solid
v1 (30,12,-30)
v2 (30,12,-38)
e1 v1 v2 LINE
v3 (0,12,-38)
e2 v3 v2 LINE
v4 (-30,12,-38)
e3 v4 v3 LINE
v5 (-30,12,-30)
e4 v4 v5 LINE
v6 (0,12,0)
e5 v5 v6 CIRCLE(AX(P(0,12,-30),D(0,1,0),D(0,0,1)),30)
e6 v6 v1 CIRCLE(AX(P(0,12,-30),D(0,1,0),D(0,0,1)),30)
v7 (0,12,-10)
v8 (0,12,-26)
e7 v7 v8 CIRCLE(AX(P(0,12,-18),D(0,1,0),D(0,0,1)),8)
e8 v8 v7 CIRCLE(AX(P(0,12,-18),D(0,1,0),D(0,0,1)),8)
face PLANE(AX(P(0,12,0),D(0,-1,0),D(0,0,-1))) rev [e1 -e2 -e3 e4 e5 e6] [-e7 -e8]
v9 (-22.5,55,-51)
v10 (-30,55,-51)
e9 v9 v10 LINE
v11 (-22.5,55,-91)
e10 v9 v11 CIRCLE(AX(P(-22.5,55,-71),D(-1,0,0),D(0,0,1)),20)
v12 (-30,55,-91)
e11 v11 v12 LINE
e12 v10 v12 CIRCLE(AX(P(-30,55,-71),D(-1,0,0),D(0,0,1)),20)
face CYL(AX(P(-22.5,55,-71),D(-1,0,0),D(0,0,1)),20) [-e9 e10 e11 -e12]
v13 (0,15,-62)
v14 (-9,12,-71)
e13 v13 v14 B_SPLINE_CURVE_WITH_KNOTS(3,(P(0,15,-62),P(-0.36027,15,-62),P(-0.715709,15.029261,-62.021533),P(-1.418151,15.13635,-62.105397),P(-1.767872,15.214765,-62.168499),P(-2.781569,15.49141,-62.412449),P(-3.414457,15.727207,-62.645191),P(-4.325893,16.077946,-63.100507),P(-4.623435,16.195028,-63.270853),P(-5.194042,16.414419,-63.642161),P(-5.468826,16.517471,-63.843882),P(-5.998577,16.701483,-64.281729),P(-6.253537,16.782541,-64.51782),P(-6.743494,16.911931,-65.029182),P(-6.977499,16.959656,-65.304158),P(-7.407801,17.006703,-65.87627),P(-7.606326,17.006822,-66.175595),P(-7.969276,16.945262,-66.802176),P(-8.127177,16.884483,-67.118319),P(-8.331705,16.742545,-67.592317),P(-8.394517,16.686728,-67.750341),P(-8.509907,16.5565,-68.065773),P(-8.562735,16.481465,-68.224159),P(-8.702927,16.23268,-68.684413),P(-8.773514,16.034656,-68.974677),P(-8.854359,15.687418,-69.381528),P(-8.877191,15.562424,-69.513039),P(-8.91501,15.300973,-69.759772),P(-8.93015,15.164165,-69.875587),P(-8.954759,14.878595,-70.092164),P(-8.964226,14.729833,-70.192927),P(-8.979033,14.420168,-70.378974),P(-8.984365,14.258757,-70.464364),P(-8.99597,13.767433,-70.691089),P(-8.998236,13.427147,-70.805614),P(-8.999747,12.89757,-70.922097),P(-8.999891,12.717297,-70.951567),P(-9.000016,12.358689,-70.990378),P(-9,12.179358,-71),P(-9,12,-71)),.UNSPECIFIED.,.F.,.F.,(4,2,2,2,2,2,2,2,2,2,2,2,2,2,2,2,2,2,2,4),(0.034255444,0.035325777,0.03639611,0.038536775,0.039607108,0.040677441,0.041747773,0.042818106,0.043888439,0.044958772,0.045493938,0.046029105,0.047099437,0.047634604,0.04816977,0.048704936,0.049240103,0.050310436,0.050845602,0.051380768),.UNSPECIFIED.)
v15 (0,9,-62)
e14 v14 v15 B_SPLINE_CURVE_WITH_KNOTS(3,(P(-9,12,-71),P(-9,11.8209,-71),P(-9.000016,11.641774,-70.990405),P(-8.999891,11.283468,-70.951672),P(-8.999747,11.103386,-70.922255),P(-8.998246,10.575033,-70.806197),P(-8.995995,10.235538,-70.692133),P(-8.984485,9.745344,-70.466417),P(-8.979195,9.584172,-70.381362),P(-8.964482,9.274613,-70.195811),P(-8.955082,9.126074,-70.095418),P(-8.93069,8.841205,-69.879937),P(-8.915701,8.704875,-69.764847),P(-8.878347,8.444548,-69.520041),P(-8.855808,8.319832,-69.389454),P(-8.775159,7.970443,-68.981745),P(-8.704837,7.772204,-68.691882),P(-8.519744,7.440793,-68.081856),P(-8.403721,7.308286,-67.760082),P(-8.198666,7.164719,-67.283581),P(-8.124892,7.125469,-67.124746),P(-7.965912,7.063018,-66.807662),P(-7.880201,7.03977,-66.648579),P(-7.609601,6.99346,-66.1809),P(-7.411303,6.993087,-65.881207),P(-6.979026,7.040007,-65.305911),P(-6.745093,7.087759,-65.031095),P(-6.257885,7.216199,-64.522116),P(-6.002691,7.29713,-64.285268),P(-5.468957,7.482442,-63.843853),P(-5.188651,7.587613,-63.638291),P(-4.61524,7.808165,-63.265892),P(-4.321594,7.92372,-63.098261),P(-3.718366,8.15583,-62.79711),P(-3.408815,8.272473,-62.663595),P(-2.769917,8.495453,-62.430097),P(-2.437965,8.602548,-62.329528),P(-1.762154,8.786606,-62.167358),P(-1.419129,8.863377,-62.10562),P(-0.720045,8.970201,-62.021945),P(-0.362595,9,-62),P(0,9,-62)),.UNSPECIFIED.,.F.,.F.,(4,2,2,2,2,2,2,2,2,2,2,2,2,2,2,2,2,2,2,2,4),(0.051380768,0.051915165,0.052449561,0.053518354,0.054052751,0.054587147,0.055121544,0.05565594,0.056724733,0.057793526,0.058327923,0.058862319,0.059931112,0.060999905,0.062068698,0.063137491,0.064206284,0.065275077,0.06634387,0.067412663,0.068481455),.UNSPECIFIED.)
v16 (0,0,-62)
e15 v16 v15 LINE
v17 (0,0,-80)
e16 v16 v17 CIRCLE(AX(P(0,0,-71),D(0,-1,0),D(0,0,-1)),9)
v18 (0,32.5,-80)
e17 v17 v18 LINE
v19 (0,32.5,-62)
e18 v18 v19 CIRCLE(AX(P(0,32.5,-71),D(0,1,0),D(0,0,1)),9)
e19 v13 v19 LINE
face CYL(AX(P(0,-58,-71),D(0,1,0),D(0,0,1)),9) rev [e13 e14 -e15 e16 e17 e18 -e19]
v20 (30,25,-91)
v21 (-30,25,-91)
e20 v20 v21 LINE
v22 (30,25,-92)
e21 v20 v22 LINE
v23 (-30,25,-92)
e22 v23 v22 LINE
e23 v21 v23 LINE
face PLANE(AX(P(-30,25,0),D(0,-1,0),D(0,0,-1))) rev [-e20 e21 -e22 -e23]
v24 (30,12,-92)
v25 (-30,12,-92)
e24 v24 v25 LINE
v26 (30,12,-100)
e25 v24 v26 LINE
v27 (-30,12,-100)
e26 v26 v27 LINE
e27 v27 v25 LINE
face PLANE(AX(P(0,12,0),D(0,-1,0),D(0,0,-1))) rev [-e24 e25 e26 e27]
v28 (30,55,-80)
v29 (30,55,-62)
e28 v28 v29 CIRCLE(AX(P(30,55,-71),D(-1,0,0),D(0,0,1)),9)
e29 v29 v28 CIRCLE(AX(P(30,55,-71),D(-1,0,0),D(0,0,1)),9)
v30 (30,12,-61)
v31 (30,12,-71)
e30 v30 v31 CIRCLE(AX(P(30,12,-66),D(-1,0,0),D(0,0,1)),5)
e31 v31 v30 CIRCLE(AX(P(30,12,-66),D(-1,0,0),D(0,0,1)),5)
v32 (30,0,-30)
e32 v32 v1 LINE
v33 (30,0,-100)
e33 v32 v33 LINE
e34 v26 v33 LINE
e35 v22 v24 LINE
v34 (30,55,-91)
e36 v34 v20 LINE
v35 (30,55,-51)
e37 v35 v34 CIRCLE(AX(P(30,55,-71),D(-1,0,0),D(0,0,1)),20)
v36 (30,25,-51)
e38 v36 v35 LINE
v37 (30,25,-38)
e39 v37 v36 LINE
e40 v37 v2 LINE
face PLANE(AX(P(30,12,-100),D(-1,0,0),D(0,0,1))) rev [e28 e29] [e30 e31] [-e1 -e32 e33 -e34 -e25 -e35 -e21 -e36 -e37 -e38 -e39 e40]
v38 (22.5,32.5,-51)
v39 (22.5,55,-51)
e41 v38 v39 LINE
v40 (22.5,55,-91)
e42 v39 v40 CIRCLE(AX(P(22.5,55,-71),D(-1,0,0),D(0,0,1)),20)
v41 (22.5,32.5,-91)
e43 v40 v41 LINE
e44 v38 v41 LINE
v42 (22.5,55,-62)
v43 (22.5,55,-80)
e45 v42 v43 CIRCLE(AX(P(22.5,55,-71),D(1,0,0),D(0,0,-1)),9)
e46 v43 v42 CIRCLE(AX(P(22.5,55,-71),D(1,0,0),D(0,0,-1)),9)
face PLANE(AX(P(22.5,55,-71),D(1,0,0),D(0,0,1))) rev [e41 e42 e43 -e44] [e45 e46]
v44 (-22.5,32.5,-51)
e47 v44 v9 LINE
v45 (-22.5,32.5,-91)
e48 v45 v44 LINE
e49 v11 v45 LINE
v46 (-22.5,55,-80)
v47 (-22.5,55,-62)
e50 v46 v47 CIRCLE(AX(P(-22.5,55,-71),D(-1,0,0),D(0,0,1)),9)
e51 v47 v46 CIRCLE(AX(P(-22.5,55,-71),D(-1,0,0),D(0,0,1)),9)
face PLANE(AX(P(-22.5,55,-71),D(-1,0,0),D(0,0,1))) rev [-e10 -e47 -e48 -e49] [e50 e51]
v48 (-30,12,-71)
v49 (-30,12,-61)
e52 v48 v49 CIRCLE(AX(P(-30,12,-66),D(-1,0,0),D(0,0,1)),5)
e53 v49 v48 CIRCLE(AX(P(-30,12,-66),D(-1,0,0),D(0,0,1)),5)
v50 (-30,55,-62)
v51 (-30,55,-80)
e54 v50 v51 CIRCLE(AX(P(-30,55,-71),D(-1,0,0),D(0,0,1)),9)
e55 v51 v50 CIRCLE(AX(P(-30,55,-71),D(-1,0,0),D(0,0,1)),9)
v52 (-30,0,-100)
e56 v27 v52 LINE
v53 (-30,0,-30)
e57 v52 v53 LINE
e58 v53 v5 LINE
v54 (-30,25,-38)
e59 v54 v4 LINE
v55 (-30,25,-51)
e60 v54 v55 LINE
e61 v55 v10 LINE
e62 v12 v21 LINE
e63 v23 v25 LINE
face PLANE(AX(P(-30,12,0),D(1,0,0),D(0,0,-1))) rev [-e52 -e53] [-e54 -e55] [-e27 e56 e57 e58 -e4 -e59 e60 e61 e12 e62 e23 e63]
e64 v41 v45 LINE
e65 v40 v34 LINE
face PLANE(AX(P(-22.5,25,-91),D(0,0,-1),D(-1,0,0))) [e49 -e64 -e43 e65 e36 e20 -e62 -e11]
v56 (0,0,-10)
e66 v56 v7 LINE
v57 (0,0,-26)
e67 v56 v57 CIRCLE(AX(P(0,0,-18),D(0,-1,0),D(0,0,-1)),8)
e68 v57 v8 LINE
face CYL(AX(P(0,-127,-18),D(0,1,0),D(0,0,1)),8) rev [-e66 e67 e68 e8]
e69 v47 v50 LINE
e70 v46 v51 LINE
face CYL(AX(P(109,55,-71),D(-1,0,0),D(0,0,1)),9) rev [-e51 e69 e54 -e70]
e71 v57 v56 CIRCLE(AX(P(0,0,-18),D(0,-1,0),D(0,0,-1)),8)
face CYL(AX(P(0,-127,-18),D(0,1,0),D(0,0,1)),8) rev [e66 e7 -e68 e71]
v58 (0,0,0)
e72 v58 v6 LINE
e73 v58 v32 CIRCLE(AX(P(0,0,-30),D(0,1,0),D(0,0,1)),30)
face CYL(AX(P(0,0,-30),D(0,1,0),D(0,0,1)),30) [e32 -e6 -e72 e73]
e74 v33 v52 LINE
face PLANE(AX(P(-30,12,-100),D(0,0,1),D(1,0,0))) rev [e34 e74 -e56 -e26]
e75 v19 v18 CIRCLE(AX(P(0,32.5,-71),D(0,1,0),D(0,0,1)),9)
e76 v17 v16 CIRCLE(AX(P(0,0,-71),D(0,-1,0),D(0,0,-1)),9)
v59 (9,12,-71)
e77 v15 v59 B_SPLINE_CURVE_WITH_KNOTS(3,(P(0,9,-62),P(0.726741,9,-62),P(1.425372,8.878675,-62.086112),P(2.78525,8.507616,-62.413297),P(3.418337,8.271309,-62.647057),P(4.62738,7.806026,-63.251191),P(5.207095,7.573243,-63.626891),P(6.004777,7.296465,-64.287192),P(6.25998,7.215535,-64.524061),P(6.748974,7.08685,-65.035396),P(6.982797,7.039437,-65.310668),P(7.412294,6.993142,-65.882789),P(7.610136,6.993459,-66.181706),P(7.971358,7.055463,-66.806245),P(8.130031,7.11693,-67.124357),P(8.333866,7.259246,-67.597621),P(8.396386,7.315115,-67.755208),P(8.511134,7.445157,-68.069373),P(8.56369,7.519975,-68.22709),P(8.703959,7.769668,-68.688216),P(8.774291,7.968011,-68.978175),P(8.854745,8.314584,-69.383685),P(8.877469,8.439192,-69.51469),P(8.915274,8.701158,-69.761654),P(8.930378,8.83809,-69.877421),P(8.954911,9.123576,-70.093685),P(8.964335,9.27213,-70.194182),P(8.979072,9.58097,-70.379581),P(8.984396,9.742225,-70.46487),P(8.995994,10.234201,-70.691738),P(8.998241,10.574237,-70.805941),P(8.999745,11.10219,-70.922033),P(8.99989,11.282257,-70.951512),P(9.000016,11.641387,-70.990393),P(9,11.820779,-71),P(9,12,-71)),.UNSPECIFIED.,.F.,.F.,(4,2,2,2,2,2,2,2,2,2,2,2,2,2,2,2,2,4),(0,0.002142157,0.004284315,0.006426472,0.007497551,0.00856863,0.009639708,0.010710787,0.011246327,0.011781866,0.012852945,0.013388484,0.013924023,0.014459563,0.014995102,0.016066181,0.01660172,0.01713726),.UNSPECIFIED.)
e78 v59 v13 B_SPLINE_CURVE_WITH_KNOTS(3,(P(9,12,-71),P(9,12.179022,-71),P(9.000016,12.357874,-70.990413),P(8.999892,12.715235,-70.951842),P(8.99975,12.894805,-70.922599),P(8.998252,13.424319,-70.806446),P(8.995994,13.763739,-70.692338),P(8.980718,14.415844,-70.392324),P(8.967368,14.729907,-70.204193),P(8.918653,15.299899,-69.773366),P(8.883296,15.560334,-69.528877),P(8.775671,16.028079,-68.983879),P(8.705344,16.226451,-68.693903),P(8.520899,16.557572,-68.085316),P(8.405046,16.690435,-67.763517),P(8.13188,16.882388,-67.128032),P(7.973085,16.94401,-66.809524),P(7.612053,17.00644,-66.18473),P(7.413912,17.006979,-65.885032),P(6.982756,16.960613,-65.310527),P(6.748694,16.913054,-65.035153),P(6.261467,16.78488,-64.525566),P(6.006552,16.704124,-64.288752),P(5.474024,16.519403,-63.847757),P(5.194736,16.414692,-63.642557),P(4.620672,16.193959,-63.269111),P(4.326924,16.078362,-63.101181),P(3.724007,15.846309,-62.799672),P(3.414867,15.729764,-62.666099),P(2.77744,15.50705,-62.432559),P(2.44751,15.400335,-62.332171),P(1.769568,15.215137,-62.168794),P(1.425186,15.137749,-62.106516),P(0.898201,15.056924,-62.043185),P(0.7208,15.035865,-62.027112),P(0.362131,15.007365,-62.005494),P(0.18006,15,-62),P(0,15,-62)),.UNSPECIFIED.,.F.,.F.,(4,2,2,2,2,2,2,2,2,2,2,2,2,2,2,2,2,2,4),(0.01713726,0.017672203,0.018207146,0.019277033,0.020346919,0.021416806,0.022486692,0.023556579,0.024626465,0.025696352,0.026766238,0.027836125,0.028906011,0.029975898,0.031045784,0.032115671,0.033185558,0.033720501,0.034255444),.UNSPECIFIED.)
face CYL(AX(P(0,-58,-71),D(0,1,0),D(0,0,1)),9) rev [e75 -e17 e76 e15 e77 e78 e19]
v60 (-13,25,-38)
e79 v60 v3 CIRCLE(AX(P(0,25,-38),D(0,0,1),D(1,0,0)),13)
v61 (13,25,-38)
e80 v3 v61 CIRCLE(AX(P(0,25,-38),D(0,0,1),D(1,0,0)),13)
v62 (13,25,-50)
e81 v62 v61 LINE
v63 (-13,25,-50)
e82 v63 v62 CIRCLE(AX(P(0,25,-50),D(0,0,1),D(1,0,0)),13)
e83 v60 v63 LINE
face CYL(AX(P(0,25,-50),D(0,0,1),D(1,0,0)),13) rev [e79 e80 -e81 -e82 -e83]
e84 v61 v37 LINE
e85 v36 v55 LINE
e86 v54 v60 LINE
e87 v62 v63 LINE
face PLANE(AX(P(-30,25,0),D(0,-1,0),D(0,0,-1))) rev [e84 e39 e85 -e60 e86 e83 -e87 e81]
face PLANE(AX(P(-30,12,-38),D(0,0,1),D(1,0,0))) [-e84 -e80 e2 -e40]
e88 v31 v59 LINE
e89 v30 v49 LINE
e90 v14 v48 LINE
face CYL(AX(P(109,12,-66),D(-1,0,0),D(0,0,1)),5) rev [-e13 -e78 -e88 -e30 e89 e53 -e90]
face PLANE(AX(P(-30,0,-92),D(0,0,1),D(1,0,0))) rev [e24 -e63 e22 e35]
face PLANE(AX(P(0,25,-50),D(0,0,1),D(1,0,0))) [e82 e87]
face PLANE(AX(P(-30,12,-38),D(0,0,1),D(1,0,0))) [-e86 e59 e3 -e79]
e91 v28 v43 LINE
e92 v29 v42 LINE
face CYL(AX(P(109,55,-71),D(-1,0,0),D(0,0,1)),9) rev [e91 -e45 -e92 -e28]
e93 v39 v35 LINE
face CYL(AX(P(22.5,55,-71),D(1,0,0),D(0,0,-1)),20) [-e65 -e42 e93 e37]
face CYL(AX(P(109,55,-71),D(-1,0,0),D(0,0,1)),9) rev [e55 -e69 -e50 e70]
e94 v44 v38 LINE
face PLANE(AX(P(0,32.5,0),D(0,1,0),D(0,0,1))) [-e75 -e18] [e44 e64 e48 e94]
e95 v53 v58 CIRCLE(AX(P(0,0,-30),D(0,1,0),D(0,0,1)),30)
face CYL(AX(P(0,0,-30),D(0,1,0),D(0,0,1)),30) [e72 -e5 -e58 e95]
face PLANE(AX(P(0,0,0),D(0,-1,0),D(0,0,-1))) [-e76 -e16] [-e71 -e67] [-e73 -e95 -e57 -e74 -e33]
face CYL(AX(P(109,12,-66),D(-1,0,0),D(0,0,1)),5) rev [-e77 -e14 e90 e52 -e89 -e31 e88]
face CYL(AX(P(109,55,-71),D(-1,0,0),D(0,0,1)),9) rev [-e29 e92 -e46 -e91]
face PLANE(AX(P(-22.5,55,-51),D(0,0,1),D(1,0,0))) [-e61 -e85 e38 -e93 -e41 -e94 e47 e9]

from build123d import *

# Parameters (mm, degrees)
BASE_PLATE_DEPTH              = 12
BASE_HOLE_DEPTH               = 12
UPRIGHT_BLOCK_SKETCH_W        = 42
UPRIGHT_BLOCK_SKETCH_H        = 12
UPRIGHT_BLOCK_DEPTH           = 60
CLEVIS_EAR_DEPTH              = 7.5
CLEVIS_EAR_EXTENSION_SKETCH_W = 45
CLEVIS_EAR_EXTENSION_SKETCH_H = 40
CLEVIS_EAR_EXTENSION_DEPTH    = 7.5
CLEVIS_PIN_BORE_SKETCH_R      = 9
CLEVIS_PIN_BORE_DEPTH         = 90.5
SADDLE_BLOCK_SKETCH_W         = 12
SADDLE_BLOCK_SKETCH_H         = 13
SADDLE_BLOCK_DEPTH            = 60
SADDLE_CUT_SKETCH_R           = 13
SADDLE_CUT_DEPTH              = 12
THROUGH_HOLE_A_SKETCH_R       = 9
THROUGH_HOLE_A_DEPTH          = 139
THROUGH_HOLE_B_SKETCH_R       = 5
THROUGH_HOLE_B_DEPTH          = 139
THROUGH_HOLE_C_SKETCH_R       = 8
THROUGH_HOLE_C_DEPTH          = 139


with BuildPart() as part:
    # Base Plate Sketch → Base Plate (new body)
    with BuildSketch(Plane(origin=(0, 0, 0), x_dir=(1, 0, 0), z_dir=(0, 1, 0))):
        Polygon((0, 0), (30, 0), (30, 100), (-30, 100), (-30, 0), align=None)
    extrude(amount=BASE_PLATE_DEPTH)

    # Base Hole Sketch → Base Hole (cut)
    with BuildSketch(Plane(origin=(0, 12, 0), x_dir=(1, 0, 0), z_dir=(0, 1, 0))):
        with BuildLine():
            ThreePointArc((1.57e-07, 0), (-21.21320338, 8.786796509), (-30, 30))
            Line((-30, 30), (-30, 0))
            Line((-30, 0), (1.57e-07, 0))
        make_face()
        with BuildLine():
            Line((30, 0), (30, 30))
            ThreePointArc((30, 30), (21.213203491, 8.78679662), (1.57e-07, 0))
            Line((1.57e-07, 0), (30, 0))
        make_face()
    extrude(amount=-BASE_HOLE_DEPTH, mode=Mode.SUBTRACT)

    # Upright Block Sketch → Upright Block (add)
    with BuildSketch(Plane(origin=(30, 0, 0), x_dir=(0, 0, -1), z_dir=(1, 0, 0))):
        Polygon((50, 12), (92, 12), (92, 25), (62, 25), (50, 25), align=None)
        with Locations((71, 6)):
            Rectangle(UPRIGHT_BLOCK_SKETCH_W, UPRIGHT_BLOCK_SKETCH_H)
    extrude(amount=-UPRIGHT_BLOCK_DEPTH)

    # Clevis Ear Sketch → Clevis Ear (add)
    with BuildSketch(Plane.ZY.offset(30)):
        with BuildLine():
            Line((-51, 55), (-51, 25))
            Line((-51, 25), (-91, 25))
            Line((-91, 25), (-91, 55))
            ThreePointArc((-91, 55), (-71, 75), (-51, 55))
        make_face()
    clevis_ear = extrude(amount=-CLEVIS_EAR_DEPTH)

    # Clevis Ear Mirror: Clevis Ear across plane
    add(clevis_ear.mirror(Plane(origin=(0, 0, 0), x_dir=(0, 0, 1), z_dir=(1, 0, 0))))

    # Clevis Ear Extension Sketch → Clevis Ear Extension (add)
    with BuildSketch(Plane(origin=(0, 25, 0), x_dir=(1, 0, 0), z_dir=(0, 1, 0))):
        with Locations((0, 71)):
            Rectangle(CLEVIS_EAR_EXTENSION_SKETCH_W, CLEVIS_EAR_EXTENSION_SKETCH_H)
    extrude(amount=CLEVIS_EAR_EXTENSION_DEPTH)

    # Clevis Pin Bore Sketch → Clevis Pin Bore (cut)
    with BuildSketch(Plane(origin=(0, 32.5, 0), x_dir=(1, 0, 0), z_dir=(0, 1, 0))):
        with Locations(Location((0, 71, 0), (0, 0, 270))):
            Circle(CLEVIS_PIN_BORE_SKETCH_R)
    extrude(amount=-CLEVIS_PIN_BORE_DEPTH, mode=Mode.SUBTRACT)

    # Saddle Block Sketch → Saddle Block (add)
    with BuildSketch(Plane(origin=(30, 0, 0), x_dir=(0, 0, -1), z_dir=(1, 0, 0))):
        with Locations((44, 18.5)):
            Rectangle(SADDLE_BLOCK_SKETCH_W, SADDLE_BLOCK_SKETCH_H)
    extrude(amount=-SADDLE_BLOCK_DEPTH)

    # Saddle Cut Sketch → Saddle Cut (cut)
    with BuildSketch(Plane.XY.offset(-38)):
        with Locations((0, 25)):
            Circle(SADDLE_CUT_SKETCH_R)
    extrude(amount=-SADDLE_CUT_DEPTH, mode=Mode.SUBTRACT)

    # Through Hole A Sketch → Through Hole A (cut)
    with BuildSketch(Plane.ZY.offset(30)):
        with Locations((-71, 55)):
            Circle(THROUGH_HOLE_A_SKETCH_R)
    extrude(amount=-THROUGH_HOLE_A_DEPTH, mode=Mode.SUBTRACT)

    # Through Hole B Sketch → Through Hole B (cut)
    with BuildSketch(Plane.ZY.offset(30)):
        with Locations((-66, 12)):
            Circle(THROUGH_HOLE_B_SKETCH_R)
    extrude(amount=-THROUGH_HOLE_B_DEPTH, mode=Mode.SUBTRACT)

    # Through Hole C Sketch → Through Hole C (cut)
    with BuildSketch(Plane(origin=(0, 12, 0), x_dir=(1, 0, 0), z_dir=(0, 1, 0))):
        with Locations(Location((0, 18, 0), (0, 0, 270))):
            Circle(THROUGH_HOLE_C_SKETCH_R)
    extrude(amount=-THROUGH_HOLE_C_DEPTH, mode=Mode.SUBTRACT)


solid = part.part
